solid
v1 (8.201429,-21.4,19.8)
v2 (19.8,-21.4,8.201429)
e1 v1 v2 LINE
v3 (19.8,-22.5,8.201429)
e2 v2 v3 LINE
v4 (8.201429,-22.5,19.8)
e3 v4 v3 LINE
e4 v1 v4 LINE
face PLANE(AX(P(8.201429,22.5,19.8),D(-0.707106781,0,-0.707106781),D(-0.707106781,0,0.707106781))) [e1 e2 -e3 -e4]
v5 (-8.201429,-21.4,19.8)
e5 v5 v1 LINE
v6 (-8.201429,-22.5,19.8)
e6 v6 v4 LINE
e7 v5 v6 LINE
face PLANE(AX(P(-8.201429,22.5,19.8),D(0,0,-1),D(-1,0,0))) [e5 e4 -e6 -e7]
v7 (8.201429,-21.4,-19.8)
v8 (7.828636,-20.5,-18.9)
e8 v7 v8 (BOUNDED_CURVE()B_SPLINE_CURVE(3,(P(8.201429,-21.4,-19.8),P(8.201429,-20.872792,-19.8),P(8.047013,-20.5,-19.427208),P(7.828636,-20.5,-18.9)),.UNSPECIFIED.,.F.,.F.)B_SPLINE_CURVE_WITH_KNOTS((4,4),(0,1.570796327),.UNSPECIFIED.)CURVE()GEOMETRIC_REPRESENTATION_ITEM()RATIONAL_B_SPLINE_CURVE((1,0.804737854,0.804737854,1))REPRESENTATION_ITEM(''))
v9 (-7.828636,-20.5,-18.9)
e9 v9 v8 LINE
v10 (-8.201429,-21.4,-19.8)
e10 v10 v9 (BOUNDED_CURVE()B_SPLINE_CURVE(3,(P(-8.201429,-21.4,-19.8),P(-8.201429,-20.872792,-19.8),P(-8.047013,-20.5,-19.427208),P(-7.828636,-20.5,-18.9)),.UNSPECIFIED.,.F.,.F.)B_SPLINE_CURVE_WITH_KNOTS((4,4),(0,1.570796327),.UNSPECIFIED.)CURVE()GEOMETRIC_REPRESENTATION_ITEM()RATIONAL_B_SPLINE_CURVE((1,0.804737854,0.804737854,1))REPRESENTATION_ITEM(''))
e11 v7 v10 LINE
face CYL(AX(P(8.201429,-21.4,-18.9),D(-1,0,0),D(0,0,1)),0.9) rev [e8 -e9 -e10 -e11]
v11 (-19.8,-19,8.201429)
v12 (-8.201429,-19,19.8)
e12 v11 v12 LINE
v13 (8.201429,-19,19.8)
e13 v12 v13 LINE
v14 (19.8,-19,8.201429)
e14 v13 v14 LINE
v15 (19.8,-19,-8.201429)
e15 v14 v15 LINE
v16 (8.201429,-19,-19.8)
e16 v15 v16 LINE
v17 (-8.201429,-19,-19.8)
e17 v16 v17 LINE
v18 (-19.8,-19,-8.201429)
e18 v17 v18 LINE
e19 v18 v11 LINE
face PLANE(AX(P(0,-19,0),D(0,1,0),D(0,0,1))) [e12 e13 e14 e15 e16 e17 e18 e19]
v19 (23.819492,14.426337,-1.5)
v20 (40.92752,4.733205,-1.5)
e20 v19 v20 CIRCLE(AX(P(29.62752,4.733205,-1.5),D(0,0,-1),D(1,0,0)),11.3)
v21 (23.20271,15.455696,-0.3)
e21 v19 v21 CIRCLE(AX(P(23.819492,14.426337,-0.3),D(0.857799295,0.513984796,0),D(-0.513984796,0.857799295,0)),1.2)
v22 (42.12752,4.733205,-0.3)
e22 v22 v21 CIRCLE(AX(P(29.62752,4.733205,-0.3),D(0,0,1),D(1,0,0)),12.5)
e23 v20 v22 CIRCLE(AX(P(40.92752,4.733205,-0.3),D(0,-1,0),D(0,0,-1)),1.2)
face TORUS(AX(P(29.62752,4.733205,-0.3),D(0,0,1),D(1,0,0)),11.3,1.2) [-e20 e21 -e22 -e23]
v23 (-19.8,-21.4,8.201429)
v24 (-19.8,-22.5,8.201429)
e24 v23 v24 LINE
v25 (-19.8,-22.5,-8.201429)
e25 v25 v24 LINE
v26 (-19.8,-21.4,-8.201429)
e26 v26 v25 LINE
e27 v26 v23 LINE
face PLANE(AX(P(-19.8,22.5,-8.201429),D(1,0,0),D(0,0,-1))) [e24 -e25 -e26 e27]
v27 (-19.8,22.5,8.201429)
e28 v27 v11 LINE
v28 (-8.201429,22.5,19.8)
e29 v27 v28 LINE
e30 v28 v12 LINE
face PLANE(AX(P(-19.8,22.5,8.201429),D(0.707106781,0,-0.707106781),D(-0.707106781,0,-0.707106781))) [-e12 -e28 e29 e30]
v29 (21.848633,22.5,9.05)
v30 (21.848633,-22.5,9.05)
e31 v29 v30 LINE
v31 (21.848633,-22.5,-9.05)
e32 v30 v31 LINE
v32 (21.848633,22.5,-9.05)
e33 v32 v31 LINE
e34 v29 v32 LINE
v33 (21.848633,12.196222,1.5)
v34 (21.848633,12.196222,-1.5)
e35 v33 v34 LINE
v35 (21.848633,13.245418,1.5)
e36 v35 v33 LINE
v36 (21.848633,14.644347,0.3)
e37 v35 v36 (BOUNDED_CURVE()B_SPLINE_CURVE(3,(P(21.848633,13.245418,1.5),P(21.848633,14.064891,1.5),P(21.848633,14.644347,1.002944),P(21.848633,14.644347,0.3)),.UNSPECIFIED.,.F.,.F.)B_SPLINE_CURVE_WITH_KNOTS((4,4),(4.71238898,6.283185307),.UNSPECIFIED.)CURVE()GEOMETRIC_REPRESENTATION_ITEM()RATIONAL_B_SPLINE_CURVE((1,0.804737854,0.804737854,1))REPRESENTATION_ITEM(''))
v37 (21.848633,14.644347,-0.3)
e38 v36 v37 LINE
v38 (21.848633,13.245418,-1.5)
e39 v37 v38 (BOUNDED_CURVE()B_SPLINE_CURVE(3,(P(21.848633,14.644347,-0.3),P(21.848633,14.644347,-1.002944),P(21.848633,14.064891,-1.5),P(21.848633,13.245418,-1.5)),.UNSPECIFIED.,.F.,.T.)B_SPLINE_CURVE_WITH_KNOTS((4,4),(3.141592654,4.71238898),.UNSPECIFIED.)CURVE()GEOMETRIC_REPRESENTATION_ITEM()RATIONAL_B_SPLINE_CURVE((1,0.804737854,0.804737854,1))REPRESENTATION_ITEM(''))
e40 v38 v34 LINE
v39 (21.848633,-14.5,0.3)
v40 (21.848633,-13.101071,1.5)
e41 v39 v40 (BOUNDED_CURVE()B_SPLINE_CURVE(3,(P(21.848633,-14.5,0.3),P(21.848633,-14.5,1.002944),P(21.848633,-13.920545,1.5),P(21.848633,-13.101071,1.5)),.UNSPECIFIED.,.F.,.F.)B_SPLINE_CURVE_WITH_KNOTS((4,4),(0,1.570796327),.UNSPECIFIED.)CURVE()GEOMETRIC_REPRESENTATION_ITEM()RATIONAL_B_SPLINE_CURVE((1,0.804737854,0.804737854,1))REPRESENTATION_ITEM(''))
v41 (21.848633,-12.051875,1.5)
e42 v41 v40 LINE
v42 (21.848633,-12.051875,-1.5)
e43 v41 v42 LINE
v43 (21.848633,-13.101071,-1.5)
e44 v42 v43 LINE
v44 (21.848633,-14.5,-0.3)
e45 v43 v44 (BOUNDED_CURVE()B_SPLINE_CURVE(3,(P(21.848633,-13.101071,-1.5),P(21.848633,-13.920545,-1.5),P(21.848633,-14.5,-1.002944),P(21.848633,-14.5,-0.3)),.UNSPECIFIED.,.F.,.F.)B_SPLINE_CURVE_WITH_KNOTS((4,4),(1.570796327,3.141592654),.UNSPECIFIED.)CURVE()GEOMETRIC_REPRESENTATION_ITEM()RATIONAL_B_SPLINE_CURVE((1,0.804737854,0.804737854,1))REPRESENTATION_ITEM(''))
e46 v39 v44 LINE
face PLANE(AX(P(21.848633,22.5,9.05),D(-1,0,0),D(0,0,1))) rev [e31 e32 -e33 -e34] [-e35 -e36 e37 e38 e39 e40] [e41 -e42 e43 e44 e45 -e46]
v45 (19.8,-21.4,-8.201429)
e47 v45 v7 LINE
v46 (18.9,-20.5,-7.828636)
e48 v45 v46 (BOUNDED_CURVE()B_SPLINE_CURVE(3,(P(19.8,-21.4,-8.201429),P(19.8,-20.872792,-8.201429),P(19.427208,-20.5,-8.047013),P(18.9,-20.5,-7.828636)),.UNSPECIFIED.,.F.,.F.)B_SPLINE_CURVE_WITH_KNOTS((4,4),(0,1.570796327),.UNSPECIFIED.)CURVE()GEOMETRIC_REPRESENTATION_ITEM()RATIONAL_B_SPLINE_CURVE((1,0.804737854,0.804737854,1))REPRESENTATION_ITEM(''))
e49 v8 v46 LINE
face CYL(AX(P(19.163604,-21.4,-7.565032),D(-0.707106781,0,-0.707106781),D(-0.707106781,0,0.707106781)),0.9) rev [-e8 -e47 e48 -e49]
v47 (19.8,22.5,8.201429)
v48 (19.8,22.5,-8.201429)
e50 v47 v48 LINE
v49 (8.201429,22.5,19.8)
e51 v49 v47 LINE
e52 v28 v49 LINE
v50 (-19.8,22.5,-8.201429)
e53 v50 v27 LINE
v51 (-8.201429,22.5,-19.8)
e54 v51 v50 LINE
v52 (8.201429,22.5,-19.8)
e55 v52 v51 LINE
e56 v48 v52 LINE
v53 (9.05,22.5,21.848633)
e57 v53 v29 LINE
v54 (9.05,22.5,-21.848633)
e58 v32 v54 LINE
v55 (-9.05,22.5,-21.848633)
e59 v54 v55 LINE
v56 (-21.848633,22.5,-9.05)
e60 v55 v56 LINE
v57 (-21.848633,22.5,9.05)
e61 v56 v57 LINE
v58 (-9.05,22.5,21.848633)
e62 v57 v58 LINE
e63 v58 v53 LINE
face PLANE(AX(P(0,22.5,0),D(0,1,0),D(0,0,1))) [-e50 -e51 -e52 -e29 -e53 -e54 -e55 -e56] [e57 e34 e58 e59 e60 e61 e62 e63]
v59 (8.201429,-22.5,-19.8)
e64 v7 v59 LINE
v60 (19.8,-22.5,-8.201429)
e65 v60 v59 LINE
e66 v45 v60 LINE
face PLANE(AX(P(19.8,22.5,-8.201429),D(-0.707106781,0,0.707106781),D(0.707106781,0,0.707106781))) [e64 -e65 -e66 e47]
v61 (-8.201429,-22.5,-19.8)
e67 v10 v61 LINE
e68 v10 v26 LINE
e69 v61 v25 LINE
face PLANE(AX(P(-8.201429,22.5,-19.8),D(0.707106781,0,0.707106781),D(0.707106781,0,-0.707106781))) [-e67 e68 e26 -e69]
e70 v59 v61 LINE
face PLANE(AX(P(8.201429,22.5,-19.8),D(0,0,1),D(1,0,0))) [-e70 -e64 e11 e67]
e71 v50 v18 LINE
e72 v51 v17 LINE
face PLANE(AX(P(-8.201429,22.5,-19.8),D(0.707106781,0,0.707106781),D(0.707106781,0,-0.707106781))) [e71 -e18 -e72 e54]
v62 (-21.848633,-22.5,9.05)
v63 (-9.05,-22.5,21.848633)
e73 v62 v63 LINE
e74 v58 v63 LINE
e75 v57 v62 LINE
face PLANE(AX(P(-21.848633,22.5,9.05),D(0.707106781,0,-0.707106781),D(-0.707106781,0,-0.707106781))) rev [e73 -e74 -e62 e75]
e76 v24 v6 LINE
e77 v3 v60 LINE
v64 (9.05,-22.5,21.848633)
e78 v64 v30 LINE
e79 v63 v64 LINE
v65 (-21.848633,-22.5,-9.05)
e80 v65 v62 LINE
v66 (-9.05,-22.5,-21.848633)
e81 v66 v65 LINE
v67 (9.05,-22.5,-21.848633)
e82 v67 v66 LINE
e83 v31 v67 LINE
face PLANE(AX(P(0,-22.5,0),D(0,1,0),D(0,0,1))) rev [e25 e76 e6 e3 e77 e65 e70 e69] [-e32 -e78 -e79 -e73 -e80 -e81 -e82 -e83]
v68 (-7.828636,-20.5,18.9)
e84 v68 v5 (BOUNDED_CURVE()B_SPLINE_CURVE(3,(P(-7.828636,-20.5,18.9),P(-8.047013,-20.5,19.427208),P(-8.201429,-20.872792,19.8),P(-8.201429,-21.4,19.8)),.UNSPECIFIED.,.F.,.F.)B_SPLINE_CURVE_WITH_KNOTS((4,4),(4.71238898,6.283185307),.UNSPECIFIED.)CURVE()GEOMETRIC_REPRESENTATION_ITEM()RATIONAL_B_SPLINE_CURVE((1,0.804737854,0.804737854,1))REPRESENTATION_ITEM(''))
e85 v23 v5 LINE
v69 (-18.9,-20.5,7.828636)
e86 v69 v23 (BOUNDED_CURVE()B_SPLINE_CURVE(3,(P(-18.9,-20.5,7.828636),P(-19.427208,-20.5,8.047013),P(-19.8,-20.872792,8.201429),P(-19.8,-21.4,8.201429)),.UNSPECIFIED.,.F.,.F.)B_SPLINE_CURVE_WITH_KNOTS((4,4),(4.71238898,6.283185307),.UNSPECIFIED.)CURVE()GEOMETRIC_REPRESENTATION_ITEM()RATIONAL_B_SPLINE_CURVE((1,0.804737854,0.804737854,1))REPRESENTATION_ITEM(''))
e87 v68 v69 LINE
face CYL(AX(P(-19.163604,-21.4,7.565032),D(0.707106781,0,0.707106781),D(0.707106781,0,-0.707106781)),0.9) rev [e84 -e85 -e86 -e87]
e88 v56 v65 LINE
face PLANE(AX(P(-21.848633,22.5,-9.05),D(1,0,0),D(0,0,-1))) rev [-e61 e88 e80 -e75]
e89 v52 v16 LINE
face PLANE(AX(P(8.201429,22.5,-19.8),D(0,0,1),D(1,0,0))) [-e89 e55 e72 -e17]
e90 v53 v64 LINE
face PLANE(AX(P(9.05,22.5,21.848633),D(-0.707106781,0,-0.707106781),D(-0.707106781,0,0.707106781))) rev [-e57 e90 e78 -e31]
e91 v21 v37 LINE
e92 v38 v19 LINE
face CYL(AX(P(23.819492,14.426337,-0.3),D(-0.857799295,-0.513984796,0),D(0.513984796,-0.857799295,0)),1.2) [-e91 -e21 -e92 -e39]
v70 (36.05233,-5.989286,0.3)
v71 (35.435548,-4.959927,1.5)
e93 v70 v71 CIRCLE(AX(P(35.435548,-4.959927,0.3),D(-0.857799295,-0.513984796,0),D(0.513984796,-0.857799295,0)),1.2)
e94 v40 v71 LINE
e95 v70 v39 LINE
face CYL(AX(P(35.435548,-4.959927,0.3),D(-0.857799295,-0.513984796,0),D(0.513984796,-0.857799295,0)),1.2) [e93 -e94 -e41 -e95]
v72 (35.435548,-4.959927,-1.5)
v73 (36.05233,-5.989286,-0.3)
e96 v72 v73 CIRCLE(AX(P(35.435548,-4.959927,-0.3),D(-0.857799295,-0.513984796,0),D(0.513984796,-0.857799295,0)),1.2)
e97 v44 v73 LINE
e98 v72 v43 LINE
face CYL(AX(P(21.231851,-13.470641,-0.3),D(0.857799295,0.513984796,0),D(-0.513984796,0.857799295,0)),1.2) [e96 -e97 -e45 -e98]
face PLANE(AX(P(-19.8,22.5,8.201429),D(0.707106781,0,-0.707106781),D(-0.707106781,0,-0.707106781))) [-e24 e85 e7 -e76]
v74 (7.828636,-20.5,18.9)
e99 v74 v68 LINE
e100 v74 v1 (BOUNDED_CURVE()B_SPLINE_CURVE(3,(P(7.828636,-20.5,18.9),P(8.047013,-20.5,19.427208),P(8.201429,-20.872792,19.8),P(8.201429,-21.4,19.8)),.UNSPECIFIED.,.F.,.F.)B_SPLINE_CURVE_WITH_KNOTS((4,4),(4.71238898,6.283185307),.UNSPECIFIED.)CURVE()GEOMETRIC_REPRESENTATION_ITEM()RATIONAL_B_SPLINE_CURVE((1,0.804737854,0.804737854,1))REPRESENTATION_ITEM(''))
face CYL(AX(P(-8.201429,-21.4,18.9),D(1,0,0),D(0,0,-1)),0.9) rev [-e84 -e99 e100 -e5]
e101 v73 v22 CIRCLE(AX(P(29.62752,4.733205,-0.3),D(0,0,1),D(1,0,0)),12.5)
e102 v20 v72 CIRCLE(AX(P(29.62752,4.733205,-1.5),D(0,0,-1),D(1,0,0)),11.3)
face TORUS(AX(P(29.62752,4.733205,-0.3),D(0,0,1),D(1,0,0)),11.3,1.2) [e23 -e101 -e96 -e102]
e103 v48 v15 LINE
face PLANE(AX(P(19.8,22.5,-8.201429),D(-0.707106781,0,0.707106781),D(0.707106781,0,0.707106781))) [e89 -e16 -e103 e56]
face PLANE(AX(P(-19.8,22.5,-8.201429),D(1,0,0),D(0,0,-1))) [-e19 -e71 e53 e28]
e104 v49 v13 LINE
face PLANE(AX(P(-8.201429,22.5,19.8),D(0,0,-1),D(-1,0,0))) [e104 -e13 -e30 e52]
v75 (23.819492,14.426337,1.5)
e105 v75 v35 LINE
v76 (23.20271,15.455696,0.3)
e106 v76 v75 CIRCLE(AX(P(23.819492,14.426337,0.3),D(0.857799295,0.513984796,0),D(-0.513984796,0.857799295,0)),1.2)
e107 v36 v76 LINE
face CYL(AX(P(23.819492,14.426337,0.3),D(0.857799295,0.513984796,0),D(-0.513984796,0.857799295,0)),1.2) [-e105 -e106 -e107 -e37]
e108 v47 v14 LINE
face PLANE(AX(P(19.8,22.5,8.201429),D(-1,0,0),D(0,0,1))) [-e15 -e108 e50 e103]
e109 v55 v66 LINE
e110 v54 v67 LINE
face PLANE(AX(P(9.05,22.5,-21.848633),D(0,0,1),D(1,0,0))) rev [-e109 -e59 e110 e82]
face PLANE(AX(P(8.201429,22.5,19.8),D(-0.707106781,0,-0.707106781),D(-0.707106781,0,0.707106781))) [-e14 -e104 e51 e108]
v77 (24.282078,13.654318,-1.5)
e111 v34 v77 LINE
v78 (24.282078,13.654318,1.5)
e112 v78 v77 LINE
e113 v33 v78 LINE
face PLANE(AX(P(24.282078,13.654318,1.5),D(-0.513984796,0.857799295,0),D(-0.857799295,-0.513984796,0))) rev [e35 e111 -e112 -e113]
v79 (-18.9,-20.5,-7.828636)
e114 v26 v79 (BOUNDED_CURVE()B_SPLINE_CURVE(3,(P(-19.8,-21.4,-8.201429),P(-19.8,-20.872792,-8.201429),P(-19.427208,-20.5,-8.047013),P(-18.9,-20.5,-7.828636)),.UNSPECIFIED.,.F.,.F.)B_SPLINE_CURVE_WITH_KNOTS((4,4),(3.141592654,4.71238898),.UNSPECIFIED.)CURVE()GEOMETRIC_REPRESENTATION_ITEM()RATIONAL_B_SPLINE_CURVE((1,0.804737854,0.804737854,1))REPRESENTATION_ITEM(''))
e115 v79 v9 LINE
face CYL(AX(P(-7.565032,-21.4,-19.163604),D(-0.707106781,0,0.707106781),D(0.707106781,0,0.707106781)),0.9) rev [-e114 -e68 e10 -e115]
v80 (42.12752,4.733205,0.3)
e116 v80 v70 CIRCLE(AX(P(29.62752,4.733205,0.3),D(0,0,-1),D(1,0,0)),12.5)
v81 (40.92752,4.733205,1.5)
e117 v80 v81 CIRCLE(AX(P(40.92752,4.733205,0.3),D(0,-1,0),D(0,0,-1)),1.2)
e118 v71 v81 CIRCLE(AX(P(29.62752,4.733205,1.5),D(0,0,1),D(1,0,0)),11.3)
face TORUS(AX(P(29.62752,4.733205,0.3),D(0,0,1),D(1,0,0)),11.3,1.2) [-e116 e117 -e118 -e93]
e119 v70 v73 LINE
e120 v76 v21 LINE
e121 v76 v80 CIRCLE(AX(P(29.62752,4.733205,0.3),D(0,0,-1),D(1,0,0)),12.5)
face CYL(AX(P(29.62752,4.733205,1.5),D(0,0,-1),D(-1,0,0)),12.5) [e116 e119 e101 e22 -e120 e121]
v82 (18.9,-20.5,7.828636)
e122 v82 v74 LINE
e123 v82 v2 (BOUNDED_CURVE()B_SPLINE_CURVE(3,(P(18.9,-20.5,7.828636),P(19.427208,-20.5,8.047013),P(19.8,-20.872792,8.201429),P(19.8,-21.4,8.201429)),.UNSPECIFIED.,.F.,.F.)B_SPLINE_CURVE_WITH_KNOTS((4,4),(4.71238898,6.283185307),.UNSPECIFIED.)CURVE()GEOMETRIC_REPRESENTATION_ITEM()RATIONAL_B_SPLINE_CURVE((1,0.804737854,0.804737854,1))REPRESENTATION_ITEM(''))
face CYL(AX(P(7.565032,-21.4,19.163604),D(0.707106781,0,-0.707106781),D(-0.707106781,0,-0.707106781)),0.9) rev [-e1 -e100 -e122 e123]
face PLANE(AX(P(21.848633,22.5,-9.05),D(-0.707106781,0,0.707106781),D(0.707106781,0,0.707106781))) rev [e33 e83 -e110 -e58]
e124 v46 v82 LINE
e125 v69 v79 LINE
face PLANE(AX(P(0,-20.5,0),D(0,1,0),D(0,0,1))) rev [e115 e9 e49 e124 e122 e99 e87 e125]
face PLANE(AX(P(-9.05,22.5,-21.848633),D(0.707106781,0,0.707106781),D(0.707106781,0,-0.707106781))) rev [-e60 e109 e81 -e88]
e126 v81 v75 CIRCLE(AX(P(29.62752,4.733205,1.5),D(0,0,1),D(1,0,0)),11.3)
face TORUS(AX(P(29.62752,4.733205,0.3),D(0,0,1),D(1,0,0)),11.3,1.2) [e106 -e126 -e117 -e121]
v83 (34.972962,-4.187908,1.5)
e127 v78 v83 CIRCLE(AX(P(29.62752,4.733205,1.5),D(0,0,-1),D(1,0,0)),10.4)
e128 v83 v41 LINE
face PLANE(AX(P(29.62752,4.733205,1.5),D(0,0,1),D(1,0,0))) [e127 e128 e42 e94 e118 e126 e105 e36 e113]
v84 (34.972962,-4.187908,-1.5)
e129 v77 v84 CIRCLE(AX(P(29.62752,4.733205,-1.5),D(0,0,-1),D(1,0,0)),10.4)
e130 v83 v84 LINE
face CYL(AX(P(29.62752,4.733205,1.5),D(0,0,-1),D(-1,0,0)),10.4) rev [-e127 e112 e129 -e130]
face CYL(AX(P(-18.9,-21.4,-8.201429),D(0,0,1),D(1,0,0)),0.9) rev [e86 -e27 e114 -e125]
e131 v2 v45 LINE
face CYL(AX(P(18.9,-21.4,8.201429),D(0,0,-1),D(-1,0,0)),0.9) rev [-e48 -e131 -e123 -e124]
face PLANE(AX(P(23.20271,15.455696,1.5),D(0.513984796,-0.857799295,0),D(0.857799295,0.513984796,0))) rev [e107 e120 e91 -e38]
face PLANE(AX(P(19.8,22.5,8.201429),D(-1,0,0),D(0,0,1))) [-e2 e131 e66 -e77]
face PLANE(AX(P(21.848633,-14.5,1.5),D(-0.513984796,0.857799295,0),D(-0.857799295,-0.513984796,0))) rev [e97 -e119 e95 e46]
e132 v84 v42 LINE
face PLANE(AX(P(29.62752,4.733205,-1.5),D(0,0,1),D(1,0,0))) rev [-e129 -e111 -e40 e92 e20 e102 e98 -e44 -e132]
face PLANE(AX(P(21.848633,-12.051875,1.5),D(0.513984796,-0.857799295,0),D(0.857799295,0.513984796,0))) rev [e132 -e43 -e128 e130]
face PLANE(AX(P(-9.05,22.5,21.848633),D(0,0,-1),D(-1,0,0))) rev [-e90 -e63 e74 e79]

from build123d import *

# Parameters (mm, degrees)
MUG_WALL_DEPTH            = 22.5
MUG_BOTTOM_DEPTH          = 1.5
BOTTOM_EDGE_FILLET_R0_9_R = 0.9
HANDLE_DEPTH              = 1.5
HANDLE_EDGE_FILLET_R1_2_R = 1.2


with BuildPart() as part:
    # Wall Profile Octagon → Mug Wall (new, symmetric)
    with BuildSketch(Plane(origin=(0, 0, 0), x_dir=(1, 0, 0), z_dir=(0, 1, 0))):
        Polygon((21.848632739, -9.05), (21.848632739, 9.05), (9.05, 21.848632739), (-9.05, 21.848632739), (-21.848632739, 9.05), (-21.848632739, -9.05), (-9.05, -21.848632739), (9.05, -21.848632739), align=None)
        Polygon((19.8, 8.201428535), (8.201428535, 19.8), (-8.201428535, 19.8), (-19.8, 8.201428535), (-19.8, -8.201428535), (-8.201428535, -19.8), (8.201428535, -19.8), (19.8, -8.201428535), align=None, mode=Mode.SUBTRACT)
    extrude(amount=MUG_WALL_DEPTH, both=True)

    # Bottom Profile Octagon → Mug Bottom (add)
    with BuildSketch(Plane(origin=(0, -20.5, 0), x_dir=(1, 0, 0), z_dir=(0, 1, 0))):
        Polygon((-19.8, 8.201428535), (-19.8, -8.201428535), (-8.201428535, -19.8), (8.201428535, -19.8), (19.8, -8.201428535), (19.8, 8.201428535), (8.201428535, 19.8), (-8.201428535, 19.8), align=None)
    extrude(amount=MUG_BOTTOM_DEPTH)

    # Bottom Edge Fillet R0.9
    bottom_edge_fillet_r0_9_edges = [part.edges().sort_by_distance(p)[0] for p in [
        (-14.000714267, -20.5, -14.000714267),
        (-19.8, -20.5, 0),
        (-14.000714267, -20.5, 14.000714267),
        (0, -20.5, 19.8),
        (14.000714267, -20.5, 14.000714267),
        (19.8, -20.5, 0),
        (14.000714267, -20.5, -14.000714267),
        (0, -20.5, -19.8),
    ]]
    fillet(bottom_edge_fillet_r0_9_edges, radius=BOTTOM_EDGE_FILLET_R0_9_R)

    # Handle Profile → Handle (add, symmetric)
    with BuildSketch(Plane.XY):
        with BuildLine():
            Line((21.848632739, -12.051874881), (34.972961948, -4.18790751))
            ThreePointArc((34.972961948, -4.18790751), (38.548632739, 10.078647028), (24.282078201, 13.65431782))
            Line((24.282078201, 13.65431782), (21.848632739, 12.196221531))
            Line((21.848632739, 12.196221531), (21.848632739, 14.644346649))
            Line((21.848632739, 14.644346649), (23.202710131, 15.455696338))
            ThreePointArc((23.202710131, 15.455696338), (40.350011258, 11.158015099), (36.052330019, -5.989286029))
            Line((36.052330019, -5.989286029), (21.848632739, -14.5))
            Line((21.848632739, -14.5), (21.848632739, -12.051874881))
        make_face()
    extrude(amount=HANDLE_DEPTH, both=True)

    # Handle Edge Fillet R1.2
    handle_edge_fillet_r1_2_edges = [part.edges().sort_by_distance(p)[0] for p in [
        (28.950481379, -10.244643014, -1.5),
        (40.350011258, 11.158015099, -1.5),
        (22.525671435, 15.050021494, -1.5),
        (28.950481379, -10.244643014, 1.5),
        (40.350011258, 11.158015099, 1.5),
        (22.525671435, 15.050021494, 1.5),
    ]]
    fillet(handle_edge_fillet_r1_2_edges, radius=HANDLE_EDGE_FILLET_R1_2_R)


solid = part.part
